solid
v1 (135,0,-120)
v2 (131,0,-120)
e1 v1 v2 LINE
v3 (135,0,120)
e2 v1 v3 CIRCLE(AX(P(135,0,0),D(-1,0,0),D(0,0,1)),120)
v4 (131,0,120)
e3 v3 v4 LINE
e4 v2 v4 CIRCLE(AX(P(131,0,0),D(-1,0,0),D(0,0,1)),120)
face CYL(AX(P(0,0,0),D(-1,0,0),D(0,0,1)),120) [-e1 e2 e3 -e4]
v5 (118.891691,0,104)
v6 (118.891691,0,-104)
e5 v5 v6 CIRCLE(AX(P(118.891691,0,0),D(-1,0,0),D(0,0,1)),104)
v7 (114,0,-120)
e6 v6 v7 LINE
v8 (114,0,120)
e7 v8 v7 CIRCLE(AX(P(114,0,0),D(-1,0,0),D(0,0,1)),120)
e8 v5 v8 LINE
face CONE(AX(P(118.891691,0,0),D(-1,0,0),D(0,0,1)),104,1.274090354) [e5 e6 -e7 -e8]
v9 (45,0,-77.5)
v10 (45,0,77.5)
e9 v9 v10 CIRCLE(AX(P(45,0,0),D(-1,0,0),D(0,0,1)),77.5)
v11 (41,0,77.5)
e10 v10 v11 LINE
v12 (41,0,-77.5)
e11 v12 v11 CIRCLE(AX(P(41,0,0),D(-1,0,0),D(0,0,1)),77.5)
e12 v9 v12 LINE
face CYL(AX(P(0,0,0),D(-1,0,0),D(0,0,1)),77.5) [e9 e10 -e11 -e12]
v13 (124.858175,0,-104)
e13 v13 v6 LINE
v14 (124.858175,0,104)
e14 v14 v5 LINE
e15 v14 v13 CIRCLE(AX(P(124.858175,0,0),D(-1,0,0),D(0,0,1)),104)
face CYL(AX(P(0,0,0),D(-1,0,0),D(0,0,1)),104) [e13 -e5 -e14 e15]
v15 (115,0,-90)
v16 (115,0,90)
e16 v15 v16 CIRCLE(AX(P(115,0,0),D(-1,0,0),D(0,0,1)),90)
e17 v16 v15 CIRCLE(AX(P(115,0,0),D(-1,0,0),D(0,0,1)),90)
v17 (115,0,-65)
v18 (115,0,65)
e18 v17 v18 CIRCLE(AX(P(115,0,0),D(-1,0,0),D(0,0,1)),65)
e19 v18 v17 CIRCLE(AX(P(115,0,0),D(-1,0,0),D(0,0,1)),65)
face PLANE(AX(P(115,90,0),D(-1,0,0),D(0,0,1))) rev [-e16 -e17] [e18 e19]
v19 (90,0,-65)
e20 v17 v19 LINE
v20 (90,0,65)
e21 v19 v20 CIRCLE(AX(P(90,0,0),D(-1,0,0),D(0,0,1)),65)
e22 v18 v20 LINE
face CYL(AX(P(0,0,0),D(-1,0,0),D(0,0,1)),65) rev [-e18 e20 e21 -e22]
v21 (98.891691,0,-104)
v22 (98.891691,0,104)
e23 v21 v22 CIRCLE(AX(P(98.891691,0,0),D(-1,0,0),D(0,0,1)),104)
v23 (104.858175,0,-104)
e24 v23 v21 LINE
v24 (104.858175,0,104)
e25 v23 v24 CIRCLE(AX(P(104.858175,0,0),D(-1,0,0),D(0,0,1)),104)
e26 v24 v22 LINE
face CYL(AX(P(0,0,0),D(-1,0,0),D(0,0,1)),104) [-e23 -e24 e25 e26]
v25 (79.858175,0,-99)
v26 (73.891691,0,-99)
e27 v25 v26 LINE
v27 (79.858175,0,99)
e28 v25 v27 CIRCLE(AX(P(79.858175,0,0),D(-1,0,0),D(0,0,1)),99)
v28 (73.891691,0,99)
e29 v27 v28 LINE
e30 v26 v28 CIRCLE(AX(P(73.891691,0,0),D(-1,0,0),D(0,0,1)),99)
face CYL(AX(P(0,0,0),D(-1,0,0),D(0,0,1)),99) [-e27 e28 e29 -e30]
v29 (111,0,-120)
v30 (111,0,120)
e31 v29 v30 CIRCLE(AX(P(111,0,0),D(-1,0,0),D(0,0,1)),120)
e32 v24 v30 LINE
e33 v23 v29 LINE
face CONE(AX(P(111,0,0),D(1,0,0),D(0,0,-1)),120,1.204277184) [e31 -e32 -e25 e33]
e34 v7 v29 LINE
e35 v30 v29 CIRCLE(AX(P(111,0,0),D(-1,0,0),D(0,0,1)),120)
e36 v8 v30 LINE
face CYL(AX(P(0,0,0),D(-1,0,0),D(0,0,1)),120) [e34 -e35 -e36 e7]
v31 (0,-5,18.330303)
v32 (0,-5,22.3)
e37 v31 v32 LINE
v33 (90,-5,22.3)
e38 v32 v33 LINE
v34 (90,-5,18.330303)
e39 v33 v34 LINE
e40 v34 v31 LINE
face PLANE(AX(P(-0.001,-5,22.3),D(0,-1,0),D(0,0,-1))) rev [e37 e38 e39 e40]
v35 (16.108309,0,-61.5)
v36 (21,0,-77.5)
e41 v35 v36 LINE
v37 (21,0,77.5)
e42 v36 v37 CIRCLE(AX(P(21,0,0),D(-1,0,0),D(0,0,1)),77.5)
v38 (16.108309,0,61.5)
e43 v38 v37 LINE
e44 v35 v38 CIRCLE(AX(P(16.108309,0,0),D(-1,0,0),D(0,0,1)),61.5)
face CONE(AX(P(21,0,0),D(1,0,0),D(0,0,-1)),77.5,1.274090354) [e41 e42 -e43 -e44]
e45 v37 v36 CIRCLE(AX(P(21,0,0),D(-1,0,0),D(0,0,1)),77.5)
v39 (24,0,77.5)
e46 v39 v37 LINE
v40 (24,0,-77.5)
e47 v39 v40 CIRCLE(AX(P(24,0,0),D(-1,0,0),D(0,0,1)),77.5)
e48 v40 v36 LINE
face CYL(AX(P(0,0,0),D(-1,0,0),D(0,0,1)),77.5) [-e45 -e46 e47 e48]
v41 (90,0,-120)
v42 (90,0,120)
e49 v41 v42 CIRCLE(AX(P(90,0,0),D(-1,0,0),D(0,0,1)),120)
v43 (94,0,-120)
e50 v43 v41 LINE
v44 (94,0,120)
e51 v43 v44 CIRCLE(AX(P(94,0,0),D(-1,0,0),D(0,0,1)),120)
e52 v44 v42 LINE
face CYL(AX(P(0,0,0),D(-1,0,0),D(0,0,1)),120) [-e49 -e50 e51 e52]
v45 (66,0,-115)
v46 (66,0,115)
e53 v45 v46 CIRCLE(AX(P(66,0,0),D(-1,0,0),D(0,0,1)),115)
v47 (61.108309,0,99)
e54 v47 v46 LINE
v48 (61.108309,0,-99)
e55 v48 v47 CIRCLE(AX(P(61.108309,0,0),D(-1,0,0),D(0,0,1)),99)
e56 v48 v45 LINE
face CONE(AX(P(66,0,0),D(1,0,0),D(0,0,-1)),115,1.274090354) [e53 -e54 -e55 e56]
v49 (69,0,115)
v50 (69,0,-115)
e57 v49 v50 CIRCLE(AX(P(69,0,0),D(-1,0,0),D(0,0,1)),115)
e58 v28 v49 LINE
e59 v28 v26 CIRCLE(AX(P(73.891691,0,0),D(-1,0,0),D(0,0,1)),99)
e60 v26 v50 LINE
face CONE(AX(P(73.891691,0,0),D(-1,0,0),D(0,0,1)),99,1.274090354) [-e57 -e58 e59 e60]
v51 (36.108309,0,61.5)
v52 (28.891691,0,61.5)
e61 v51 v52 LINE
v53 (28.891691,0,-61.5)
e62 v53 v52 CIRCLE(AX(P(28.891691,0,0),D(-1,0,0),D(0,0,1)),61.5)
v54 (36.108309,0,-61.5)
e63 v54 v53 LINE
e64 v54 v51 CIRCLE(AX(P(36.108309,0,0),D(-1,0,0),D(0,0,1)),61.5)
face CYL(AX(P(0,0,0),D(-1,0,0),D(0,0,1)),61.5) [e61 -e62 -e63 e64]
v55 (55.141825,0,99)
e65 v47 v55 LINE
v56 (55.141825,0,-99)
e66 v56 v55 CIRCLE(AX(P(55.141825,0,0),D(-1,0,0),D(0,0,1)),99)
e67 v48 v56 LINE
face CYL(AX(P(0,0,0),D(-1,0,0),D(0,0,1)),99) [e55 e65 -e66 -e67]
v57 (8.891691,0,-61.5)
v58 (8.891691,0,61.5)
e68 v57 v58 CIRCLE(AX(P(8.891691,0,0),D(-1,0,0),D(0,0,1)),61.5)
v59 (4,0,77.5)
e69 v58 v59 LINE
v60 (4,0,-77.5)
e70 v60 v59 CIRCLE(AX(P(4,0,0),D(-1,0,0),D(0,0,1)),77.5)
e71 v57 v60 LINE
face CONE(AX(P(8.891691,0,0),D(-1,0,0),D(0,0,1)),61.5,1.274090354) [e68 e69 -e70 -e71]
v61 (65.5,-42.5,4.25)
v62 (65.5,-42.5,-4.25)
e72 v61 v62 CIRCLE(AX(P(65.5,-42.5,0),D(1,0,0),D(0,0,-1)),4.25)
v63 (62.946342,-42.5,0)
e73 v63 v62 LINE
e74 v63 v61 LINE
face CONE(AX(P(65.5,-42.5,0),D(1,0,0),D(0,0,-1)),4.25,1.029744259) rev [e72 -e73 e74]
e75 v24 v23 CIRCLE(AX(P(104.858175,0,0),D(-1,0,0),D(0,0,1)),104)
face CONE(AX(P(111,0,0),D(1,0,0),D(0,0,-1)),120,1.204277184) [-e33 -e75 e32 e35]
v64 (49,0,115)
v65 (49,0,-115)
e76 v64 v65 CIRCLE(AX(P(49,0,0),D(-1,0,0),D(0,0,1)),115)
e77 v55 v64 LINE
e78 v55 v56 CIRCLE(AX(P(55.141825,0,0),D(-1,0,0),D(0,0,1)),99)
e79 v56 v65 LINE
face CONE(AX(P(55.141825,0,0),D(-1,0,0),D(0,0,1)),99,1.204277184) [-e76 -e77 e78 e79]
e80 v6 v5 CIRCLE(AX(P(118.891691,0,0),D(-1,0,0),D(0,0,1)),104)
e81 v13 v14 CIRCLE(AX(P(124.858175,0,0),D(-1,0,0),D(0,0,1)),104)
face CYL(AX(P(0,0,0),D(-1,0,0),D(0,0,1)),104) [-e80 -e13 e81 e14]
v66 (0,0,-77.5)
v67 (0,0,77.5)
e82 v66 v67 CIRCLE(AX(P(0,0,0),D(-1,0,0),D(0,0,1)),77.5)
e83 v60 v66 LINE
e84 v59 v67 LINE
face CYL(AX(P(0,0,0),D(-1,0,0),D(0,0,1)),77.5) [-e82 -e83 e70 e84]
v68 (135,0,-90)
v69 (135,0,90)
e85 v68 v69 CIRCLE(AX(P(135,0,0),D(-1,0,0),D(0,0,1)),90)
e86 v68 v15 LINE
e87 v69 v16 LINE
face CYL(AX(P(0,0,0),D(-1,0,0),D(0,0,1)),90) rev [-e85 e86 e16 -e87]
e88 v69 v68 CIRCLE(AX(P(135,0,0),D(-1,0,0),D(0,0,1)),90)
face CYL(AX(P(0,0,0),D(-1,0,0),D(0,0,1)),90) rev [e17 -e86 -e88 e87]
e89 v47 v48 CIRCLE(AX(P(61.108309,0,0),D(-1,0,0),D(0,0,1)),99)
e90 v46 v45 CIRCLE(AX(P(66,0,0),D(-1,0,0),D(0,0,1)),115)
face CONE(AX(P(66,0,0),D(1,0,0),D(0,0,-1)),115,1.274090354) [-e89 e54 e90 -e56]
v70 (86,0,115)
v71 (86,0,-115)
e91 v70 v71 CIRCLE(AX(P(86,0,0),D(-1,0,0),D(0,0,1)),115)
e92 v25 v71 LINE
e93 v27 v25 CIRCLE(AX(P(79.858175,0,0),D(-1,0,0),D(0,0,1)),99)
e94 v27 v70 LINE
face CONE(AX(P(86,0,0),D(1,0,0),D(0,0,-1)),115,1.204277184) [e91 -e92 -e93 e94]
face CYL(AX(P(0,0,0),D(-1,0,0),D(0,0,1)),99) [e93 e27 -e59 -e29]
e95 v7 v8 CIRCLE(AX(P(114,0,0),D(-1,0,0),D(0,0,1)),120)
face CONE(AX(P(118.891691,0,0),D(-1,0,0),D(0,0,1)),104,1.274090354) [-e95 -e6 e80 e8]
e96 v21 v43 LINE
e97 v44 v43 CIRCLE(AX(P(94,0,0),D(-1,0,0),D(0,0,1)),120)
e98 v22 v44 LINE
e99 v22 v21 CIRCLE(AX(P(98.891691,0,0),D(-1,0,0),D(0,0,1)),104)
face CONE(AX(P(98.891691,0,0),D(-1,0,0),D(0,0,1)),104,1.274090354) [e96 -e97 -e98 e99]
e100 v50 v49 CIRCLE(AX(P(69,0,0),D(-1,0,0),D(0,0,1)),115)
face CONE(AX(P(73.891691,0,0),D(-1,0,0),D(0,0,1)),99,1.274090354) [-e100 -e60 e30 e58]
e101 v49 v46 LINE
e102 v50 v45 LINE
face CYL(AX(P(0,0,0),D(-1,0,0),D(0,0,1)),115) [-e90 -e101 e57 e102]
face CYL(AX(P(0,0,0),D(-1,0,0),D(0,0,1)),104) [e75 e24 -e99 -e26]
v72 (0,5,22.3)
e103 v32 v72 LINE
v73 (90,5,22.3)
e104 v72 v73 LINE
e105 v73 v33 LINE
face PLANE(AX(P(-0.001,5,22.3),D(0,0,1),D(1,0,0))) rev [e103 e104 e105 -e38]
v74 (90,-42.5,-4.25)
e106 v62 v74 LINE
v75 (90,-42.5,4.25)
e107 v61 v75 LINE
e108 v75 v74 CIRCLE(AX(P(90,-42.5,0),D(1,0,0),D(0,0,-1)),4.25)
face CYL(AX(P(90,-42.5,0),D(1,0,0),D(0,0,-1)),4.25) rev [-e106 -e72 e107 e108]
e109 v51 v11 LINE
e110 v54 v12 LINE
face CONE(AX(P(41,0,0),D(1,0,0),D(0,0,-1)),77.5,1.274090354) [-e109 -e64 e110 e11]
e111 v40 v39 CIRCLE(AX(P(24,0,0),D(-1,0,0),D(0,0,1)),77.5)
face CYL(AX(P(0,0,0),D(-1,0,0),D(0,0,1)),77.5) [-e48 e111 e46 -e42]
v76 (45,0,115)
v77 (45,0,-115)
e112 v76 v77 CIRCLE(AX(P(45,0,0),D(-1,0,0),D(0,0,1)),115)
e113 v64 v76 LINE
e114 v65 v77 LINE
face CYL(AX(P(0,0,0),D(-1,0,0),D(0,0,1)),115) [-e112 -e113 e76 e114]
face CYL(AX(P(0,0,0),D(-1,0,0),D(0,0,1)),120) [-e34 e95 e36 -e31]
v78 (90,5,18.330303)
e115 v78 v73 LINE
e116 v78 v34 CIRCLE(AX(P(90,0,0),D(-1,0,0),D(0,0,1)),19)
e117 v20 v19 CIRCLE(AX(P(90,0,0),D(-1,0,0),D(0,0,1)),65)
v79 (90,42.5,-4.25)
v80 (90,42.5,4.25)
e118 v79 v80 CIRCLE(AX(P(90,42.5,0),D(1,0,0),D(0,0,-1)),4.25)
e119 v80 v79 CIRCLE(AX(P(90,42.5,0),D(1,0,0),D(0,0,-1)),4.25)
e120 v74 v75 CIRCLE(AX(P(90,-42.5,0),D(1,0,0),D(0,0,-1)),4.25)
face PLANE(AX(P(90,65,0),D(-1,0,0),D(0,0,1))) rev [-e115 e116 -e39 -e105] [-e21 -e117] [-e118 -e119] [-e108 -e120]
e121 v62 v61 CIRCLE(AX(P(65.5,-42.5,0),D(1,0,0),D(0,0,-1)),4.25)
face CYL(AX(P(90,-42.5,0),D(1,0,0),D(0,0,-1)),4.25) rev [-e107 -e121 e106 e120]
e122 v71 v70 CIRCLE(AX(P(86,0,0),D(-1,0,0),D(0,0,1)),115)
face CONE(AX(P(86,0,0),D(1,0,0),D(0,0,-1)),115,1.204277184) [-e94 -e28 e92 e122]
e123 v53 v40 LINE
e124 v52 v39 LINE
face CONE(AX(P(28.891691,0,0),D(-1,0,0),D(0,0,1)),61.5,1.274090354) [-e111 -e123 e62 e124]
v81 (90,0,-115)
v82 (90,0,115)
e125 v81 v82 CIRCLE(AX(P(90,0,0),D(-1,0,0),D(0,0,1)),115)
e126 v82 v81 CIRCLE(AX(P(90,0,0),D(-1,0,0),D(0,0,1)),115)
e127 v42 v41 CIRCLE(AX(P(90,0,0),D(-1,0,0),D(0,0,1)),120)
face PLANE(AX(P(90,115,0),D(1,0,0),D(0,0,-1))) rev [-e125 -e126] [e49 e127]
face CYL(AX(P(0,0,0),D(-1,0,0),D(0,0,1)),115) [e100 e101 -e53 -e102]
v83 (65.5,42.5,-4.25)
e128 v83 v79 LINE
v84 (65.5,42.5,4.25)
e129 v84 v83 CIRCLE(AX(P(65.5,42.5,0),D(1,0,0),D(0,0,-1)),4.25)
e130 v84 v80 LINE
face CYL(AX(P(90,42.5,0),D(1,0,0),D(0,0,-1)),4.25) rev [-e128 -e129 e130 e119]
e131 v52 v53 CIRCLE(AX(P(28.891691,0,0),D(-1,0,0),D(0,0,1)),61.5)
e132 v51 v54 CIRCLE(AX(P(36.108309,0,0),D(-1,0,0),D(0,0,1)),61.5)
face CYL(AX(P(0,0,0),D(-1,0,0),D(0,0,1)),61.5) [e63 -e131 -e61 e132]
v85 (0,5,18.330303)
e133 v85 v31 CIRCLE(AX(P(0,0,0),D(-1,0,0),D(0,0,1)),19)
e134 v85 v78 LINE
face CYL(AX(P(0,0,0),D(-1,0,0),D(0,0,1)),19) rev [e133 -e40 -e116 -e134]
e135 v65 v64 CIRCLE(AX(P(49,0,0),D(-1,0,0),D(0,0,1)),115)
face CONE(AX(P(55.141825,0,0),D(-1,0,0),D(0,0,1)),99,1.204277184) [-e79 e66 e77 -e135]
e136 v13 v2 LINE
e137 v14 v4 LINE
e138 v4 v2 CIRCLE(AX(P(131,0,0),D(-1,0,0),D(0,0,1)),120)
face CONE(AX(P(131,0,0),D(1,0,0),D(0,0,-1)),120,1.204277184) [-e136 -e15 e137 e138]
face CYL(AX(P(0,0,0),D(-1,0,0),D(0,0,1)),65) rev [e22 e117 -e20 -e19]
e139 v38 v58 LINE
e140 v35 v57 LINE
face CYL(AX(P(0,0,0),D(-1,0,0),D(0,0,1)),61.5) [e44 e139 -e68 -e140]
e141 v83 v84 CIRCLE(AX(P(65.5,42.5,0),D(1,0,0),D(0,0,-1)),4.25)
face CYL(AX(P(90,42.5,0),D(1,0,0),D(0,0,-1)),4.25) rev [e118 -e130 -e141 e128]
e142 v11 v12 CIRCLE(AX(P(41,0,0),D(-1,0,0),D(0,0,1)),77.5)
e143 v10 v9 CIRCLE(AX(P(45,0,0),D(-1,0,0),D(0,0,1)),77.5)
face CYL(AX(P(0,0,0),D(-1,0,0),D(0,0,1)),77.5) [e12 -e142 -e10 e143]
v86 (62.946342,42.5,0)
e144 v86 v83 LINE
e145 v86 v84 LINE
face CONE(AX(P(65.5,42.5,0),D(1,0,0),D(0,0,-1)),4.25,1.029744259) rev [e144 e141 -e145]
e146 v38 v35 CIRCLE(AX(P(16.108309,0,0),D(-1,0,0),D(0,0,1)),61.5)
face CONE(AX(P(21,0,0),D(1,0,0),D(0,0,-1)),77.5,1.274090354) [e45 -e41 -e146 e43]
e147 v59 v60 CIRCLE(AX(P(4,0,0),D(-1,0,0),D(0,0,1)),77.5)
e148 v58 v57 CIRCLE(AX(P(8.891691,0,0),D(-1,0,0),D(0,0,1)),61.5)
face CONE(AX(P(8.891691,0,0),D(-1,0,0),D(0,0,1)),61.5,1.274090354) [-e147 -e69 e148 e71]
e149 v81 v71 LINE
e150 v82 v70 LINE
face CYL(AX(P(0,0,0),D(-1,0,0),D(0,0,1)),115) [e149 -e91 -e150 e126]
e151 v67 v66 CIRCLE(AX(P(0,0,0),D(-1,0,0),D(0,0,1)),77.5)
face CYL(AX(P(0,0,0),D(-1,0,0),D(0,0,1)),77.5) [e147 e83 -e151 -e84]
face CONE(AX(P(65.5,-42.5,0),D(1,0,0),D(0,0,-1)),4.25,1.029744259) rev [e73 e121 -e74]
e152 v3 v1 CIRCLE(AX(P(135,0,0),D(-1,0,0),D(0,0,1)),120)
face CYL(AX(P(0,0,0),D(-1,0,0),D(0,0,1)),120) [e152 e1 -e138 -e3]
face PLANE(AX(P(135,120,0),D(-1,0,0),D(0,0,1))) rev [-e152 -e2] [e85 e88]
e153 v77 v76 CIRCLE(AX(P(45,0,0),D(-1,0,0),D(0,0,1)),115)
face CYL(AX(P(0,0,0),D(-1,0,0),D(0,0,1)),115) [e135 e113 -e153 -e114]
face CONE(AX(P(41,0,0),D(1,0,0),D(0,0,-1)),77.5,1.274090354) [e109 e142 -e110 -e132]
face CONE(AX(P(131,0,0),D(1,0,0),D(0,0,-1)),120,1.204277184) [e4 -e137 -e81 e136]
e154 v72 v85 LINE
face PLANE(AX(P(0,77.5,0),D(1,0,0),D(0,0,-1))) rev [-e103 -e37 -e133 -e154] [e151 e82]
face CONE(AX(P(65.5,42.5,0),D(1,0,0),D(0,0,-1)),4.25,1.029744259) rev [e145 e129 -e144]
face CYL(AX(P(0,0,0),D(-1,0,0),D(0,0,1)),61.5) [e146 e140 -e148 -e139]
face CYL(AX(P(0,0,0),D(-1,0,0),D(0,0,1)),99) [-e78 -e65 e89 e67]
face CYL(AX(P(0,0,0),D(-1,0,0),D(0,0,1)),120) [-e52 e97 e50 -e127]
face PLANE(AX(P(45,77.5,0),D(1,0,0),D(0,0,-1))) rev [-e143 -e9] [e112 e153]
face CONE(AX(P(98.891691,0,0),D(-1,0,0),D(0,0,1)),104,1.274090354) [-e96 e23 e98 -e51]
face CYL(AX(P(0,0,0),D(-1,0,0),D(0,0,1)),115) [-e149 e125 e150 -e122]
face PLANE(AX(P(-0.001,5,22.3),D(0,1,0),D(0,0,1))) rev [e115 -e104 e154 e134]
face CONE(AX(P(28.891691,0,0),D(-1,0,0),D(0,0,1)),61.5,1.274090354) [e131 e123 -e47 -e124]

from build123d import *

# Parameters (mm, degrees)
CUT_EXTRUDE_1_REACH     = 194.094
SKETCH_2_W              = 3.96969722
SKETCH_2_H              = 10
HOLE_WIZARD_M10_2_D     = 8.5
HOLE_WIZARD_M10_2_DEPTH = 24.5
HOLE_WIZARD_M10_2_TIP   = 2.553657631


with BuildPart() as part:
    # 草图1 → 旋转1 (revolve)
    with BuildSketch(Plane.XY, mode=Mode.PRIVATE) as revolve_1_sk:
        Polygon((0, 77.5), (0, 19), (90, 19), (90, 65), (115, 65), (115, 90), (135, 90), (135, 120), (131, 120), (124.858175439, 104), (118.891690903, 104), (114, 120), (111, 120), (104.858175439, 104), (98.891690903, 104), (94, 120), (90, 120), (90, 115), (86, 115), (79.858175439, 99), (73.891690903, 99), (69, 115), (66, 115), (61.108309097, 99), (55.141824561, 99), (49, 115), (45, 115), (45, 77.5), (41, 77.5), (36.108309097, 61.5), (28.891690903, 61.5), (24, 77.5), (21, 77.5), (16.108309097, 61.5), (8.891690903, 61.5), (4, 77.5), align=None)
    revolve(revolve_1_sk.sketch.rotate(Axis((0, 0, 0), (1, 0, 0)), 90), axis=Axis((0, 0, 0), (1, 0, 0)))

    # 草图2 → 切除-拉伸1 (cut, up to next)
    with BuildSketch(Plane(origin=(90, 0, 0), x_dir=(0, 0, -1), z_dir=(1, 0, 0)), mode=Mode.PRIVATE) as cut_extrude_1_sk1:
        with Locations((-20.31515139, 0)):
            Rectangle(SKETCH_2_W, SKETCH_2_H)
    cut_extrude_1_tool1 = extrude(cut_extrude_1_sk1.sketch, amount=-CUT_EXTRUDE_1_REACH, mode=Mode.PRIVATE) & part.part
    add(cut_extrude_1_tool1.solids().sort_by_distance((90, 0, 20.315151))[0], mode=Mode.SUBTRACT)

    # M10 螺纹孔2
    with Locations(Plane(origin=(90, 0, 0), x_dir=(0, 0, -1), z_dir=(1, 0, 0))):
        with Locations((0, 42.5), (0, -42.5)):
            Hole(HOLE_WIZARD_M10_2_D / 2, depth=HOLE_WIZARD_M10_2_DEPTH)
            with Locations((0, 0, -(HOLE_WIZARD_M10_2_DEPTH + HOLE_WIZARD_M10_2_TIP / 2))):  # 118° drill point
                Cone(0, HOLE_WIZARD_M10_2_D / 2, HOLE_WIZARD_M10_2_TIP, mode=Mode.SUBTRACT)


solid = part.part
